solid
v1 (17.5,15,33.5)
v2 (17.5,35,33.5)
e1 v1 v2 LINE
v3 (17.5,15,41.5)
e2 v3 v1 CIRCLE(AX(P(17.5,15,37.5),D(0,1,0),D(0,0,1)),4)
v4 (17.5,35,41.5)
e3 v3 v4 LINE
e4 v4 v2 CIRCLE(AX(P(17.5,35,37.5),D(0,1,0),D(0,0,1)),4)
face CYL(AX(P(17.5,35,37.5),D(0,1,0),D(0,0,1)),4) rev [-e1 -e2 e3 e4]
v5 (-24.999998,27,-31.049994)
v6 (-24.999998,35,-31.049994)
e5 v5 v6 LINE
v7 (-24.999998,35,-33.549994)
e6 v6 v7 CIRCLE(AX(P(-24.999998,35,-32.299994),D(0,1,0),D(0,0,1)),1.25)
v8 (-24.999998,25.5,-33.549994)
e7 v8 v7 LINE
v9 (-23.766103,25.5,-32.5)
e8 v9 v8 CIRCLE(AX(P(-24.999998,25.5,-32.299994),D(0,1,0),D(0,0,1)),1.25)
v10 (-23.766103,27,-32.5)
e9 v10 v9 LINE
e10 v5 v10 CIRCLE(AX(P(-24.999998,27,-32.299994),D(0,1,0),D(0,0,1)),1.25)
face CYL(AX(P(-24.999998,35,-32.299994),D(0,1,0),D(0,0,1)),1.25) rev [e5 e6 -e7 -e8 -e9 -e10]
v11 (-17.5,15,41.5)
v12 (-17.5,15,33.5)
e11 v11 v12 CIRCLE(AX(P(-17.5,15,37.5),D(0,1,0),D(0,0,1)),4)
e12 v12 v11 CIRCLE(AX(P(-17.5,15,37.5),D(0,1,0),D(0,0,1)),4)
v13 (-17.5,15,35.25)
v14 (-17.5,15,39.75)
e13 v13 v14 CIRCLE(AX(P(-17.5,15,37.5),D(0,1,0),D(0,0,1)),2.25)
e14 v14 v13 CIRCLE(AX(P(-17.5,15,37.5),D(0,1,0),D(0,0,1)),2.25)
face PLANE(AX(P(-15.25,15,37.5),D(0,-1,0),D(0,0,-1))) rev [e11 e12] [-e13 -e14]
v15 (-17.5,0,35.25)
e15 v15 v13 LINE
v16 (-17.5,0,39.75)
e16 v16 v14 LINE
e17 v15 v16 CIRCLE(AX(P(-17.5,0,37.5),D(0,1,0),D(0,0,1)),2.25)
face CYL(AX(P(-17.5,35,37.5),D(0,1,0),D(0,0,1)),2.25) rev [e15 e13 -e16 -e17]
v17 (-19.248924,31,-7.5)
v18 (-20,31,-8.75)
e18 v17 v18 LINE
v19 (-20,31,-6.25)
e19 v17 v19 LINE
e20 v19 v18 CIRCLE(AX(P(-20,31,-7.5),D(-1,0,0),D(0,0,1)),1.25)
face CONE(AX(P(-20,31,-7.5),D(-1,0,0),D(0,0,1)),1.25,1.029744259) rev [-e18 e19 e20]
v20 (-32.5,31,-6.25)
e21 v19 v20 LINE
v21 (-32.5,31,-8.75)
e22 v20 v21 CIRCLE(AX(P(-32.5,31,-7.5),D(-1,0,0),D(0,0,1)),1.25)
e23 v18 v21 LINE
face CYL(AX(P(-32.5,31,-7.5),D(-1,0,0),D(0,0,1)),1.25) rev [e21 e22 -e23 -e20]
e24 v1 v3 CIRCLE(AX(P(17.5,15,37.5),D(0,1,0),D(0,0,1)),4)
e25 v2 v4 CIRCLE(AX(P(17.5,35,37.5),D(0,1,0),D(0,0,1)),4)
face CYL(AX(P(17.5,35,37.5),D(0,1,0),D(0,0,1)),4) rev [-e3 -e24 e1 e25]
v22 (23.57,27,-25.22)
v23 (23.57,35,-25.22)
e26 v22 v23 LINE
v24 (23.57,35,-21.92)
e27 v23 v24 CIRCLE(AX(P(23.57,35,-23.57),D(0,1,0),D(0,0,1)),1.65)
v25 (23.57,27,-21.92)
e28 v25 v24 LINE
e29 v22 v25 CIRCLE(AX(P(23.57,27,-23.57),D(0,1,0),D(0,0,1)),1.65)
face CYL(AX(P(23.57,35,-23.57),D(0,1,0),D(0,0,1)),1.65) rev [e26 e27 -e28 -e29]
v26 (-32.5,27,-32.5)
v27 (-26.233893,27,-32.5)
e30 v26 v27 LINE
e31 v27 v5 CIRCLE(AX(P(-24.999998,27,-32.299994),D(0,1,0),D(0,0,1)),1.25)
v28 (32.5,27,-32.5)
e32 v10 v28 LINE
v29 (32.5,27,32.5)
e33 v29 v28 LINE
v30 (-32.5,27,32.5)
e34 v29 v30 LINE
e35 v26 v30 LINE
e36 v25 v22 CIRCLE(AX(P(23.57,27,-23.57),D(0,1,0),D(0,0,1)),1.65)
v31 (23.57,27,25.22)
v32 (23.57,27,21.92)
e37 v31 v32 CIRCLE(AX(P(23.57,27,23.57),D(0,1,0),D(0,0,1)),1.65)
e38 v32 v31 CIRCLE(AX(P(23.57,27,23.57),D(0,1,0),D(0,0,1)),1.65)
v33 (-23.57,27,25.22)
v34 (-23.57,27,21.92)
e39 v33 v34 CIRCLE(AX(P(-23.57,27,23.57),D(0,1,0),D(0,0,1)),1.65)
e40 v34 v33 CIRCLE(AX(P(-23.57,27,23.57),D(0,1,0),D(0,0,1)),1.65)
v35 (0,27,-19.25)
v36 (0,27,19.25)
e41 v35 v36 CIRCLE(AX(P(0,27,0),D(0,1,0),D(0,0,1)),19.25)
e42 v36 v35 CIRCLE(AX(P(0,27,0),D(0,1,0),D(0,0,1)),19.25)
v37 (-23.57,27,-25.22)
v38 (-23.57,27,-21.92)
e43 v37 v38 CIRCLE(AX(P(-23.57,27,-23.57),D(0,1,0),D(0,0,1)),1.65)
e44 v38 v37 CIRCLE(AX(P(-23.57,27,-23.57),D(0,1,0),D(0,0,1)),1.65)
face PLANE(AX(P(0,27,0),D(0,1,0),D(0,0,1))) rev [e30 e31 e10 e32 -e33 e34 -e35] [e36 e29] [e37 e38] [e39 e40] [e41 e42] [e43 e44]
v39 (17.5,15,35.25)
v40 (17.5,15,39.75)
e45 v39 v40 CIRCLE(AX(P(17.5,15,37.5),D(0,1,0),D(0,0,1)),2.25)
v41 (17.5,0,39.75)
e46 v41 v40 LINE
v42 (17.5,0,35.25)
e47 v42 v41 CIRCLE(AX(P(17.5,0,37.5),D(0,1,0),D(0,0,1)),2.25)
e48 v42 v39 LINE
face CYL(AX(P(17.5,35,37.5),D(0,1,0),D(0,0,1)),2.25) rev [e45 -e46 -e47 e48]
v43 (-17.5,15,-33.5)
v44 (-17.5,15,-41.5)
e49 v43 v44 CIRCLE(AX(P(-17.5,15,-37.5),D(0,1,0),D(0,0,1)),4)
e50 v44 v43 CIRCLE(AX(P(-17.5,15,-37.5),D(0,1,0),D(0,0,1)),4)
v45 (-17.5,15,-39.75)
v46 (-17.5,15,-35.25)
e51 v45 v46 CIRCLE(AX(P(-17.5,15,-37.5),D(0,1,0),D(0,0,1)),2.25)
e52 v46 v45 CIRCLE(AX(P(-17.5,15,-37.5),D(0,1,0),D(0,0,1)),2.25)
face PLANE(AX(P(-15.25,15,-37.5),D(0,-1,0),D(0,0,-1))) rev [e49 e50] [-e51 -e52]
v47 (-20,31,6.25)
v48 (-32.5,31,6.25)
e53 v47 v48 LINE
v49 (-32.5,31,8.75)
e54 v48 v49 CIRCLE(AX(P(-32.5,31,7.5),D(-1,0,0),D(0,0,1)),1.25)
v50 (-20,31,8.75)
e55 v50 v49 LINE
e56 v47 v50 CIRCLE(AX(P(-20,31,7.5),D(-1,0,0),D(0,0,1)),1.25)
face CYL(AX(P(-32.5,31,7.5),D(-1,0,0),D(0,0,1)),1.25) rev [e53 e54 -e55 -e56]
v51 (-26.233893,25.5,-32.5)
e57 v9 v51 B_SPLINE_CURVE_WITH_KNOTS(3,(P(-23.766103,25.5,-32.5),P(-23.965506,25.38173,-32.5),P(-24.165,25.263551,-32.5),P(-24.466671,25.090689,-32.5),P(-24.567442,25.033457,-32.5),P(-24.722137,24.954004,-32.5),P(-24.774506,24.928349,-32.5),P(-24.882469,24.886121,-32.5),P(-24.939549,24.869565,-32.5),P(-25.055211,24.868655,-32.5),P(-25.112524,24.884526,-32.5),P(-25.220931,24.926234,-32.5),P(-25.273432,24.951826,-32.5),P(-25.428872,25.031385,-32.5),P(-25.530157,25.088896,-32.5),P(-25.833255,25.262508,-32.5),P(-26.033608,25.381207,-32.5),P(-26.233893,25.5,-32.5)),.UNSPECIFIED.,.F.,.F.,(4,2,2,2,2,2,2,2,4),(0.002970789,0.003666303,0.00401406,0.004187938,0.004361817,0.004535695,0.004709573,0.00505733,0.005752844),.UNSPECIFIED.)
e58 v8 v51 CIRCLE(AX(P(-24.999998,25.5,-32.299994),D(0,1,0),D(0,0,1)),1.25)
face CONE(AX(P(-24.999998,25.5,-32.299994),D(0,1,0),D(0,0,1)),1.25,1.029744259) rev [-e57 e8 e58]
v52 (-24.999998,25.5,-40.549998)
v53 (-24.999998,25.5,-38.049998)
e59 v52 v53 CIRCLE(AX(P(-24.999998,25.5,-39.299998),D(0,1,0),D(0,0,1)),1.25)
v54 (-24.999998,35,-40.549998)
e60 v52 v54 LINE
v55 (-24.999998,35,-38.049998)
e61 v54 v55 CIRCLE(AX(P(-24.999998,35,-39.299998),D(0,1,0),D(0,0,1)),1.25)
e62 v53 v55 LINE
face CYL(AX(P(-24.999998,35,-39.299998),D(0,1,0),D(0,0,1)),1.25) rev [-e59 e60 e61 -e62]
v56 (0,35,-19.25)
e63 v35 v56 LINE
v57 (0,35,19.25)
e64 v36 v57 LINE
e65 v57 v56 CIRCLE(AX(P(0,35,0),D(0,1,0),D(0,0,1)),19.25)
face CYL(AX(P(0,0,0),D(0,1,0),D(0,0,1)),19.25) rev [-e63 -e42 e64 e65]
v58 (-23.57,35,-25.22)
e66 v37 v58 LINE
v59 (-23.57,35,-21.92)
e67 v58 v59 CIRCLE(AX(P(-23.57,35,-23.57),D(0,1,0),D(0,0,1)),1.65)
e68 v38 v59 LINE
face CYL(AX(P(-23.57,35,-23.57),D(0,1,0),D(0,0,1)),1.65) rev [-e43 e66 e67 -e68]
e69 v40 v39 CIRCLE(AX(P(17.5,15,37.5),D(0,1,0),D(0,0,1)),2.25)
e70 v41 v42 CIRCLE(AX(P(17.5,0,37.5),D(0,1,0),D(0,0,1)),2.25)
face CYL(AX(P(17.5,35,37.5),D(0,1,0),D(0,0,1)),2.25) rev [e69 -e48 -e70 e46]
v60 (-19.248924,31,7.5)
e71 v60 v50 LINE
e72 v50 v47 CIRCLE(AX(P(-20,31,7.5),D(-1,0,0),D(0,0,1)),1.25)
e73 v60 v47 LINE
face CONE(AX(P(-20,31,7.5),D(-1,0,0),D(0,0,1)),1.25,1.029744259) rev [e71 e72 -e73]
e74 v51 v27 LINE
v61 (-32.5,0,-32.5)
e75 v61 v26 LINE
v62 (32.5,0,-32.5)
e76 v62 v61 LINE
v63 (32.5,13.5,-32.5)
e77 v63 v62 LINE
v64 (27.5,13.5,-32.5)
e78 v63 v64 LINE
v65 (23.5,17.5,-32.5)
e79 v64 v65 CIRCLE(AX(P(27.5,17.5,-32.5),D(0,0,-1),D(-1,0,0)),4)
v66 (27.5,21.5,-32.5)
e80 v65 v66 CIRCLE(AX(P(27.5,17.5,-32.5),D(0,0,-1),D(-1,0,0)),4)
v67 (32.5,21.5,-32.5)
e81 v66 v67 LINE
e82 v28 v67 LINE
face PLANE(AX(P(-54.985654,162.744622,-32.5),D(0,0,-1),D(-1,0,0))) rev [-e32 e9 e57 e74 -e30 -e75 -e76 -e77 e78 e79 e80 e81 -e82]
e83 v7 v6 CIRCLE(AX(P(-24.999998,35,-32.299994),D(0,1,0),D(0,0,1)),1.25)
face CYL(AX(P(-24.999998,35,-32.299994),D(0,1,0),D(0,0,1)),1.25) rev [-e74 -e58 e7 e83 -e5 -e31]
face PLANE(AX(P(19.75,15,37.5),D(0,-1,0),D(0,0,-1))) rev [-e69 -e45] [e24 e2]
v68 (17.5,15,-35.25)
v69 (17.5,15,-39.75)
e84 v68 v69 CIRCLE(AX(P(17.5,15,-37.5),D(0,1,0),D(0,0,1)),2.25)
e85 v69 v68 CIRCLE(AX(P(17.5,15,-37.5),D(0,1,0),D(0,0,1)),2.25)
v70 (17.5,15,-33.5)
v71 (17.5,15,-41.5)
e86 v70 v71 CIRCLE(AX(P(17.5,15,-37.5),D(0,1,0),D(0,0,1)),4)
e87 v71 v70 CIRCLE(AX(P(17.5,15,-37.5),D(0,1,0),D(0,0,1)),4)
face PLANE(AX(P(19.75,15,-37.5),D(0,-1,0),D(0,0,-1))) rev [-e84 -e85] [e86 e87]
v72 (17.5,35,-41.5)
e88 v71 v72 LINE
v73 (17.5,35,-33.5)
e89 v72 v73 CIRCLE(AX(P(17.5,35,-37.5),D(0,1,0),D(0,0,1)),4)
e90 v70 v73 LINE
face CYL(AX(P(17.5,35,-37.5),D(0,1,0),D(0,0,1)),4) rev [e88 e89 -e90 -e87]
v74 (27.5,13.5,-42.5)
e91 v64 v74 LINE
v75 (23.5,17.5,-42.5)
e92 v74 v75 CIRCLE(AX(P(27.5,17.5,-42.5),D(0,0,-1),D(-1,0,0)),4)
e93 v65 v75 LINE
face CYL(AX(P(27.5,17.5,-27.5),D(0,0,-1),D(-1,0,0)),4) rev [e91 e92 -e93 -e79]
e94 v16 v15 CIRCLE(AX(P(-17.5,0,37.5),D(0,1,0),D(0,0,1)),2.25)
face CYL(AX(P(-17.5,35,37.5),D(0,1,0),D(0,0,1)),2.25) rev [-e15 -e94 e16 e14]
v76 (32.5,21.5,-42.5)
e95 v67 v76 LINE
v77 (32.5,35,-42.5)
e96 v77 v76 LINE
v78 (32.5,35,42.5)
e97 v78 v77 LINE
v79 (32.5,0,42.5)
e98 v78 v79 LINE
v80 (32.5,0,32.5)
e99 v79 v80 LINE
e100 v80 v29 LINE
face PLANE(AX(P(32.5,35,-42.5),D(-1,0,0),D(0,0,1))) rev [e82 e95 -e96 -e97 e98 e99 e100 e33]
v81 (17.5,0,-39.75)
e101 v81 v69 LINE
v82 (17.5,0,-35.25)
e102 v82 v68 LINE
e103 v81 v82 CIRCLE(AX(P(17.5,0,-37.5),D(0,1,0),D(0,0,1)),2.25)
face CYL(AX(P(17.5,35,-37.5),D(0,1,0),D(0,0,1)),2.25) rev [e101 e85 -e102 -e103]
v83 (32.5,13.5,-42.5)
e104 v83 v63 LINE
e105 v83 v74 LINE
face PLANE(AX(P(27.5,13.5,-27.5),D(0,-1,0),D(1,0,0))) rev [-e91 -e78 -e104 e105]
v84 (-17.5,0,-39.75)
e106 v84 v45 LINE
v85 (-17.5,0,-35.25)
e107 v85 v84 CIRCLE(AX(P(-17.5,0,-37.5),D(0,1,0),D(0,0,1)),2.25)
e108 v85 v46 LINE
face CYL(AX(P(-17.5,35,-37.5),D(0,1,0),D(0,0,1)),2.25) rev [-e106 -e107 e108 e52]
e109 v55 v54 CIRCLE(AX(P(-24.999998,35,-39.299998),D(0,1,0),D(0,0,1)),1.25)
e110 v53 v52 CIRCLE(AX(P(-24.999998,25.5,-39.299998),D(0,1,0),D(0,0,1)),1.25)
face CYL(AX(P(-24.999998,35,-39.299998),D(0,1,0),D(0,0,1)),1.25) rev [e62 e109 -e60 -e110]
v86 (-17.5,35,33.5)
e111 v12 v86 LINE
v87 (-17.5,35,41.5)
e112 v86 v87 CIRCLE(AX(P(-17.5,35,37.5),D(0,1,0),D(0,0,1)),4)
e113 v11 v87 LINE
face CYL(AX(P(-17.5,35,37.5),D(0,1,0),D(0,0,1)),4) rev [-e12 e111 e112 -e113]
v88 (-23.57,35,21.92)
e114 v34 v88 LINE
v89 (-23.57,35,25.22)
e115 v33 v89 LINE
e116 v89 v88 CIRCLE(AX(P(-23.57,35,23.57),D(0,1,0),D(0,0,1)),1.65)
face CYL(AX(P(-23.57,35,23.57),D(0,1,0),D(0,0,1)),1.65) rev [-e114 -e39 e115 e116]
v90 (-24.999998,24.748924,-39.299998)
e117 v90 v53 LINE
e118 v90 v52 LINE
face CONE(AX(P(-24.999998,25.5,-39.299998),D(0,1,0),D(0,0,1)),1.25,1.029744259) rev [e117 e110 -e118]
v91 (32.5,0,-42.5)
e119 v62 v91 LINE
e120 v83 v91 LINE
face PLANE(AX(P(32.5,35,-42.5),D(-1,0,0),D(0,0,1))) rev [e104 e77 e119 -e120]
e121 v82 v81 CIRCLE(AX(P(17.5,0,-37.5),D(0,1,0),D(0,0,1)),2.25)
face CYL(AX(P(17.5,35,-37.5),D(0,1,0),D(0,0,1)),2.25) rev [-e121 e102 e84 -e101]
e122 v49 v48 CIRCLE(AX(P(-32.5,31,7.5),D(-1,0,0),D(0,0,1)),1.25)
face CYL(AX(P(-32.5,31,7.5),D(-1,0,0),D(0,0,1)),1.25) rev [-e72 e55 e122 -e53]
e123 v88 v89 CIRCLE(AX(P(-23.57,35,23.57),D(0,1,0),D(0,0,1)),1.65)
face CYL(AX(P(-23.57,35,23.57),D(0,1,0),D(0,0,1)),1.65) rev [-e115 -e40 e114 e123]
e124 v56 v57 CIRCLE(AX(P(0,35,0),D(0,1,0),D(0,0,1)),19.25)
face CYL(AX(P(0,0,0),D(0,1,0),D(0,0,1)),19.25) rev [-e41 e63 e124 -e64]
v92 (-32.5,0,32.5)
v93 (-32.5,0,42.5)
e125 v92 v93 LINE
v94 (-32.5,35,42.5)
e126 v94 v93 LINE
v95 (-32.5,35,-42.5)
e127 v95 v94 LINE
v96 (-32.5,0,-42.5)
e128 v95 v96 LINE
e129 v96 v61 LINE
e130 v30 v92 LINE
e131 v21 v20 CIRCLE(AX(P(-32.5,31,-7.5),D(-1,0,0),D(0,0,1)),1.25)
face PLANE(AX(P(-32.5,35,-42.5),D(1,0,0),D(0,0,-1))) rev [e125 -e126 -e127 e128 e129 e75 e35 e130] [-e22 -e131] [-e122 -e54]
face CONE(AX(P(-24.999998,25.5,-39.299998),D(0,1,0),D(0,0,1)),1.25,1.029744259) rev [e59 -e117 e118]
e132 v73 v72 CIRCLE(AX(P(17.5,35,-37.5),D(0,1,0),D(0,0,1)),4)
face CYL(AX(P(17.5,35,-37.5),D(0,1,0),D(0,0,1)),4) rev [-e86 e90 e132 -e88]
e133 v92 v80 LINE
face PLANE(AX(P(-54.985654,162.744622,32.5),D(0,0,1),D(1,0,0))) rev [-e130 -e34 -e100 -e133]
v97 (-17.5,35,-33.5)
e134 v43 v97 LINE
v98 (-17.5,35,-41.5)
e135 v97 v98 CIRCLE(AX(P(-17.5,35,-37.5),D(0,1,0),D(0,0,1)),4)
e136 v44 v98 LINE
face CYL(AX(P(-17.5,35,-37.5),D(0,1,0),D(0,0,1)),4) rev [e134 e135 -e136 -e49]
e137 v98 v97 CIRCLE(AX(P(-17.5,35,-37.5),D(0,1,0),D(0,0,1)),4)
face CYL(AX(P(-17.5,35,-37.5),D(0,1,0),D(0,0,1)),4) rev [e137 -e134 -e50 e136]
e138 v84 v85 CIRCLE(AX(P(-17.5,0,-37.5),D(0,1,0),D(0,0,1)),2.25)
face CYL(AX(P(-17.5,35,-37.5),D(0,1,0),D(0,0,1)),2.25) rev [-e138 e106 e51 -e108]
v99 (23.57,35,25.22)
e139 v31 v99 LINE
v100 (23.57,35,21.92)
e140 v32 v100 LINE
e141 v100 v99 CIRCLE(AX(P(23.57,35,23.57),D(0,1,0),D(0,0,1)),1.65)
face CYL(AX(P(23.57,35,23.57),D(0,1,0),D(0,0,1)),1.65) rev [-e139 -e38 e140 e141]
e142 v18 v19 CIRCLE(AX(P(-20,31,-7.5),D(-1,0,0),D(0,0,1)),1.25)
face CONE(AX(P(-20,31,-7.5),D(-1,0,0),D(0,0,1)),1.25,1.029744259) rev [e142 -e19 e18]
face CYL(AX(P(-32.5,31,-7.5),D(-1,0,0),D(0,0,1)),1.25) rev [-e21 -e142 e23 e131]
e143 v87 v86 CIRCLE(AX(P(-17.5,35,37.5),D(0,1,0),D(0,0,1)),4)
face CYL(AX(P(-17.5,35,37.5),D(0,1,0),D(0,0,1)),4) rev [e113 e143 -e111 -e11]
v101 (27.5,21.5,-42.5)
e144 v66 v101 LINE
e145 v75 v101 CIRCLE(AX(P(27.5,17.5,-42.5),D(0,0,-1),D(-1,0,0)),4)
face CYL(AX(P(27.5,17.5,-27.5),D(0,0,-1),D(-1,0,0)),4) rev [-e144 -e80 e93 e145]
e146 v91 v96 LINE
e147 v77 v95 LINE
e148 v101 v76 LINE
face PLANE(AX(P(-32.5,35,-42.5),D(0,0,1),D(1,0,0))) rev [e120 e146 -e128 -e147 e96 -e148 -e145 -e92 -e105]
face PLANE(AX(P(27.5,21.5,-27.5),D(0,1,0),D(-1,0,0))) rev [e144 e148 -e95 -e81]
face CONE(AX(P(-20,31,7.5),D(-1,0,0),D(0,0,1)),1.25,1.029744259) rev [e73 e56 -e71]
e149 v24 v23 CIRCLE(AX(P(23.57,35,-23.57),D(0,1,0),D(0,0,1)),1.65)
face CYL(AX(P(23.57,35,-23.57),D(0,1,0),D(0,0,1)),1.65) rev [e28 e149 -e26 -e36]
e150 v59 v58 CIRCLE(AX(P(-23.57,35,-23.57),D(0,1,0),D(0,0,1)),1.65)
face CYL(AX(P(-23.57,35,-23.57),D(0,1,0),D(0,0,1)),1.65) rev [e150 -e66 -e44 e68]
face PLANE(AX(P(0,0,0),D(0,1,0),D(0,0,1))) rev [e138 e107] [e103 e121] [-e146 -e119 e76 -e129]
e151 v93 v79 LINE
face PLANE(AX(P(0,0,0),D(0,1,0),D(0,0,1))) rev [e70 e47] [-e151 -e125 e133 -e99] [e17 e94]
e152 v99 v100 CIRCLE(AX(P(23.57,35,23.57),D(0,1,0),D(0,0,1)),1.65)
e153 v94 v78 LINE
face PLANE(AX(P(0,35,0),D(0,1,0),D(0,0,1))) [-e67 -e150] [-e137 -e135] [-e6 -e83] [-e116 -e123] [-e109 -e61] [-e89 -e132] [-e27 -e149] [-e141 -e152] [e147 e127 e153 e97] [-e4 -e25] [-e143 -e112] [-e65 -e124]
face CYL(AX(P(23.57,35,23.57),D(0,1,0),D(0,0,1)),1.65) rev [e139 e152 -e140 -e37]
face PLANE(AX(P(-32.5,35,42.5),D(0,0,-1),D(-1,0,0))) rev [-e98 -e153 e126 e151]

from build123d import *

# Parameters (mm, degrees)
SKETCH_1_W                = 65
SKETCH_1_H                = 85
EXTRUDE_1_DEPTH           = 35
SKETCH_2_W                = 109.971307268
SKETCH_2_H                = 65
CUT_EXTRUDE_1_DEPTH       = 27
SKETCH_3_R                = 19.25
CUT_EXTRUDE_2_DEPTH       = 64.933559263
HOLE_WIZARD_M4_1_D        = 3.3
HOLE_WIZARD_M3_1_D        = 2.5
HOLE_WIZARD_M3_1_DEPTH    = 12.5
HOLE_WIZARD_M3_1_TIP      = 0.751075774
CUT_EXTRUDE_3_DEPTH       = 15
HOLE_WIZARD_1_D           = 4.5
HOLE_WIZARD_1_CBORE_D     = 8
HOLE_WIZARD_1_CBORE_DEPTH = 20
HOLE_WIZARD_M3_3_D        = 2.5
HOLE_WIZARD_M3_3_DEPTH    = 9.5
HOLE_WIZARD_M3_3_TIP      = 0.751075774


with BuildPart() as part:
    # 草图1 → 凸台-拉伸1 (new body)
    with BuildSketch(Plane(origin=(0, 0, 0), x_dir=(1, 0, 0), z_dir=(0, 1, 0))):
        Rectangle(SKETCH_1_W, SKETCH_1_H)
    extrude(amount=EXTRUDE_1_DEPTH)

    # 草图2 → 切除-拉伸1 (cut)
    with BuildSketch(Plane.XZ):
        Rectangle(SKETCH_2_W, SKETCH_2_H)
    extrude(amount=-CUT_EXTRUDE_1_DEPTH, mode=Mode.SUBTRACT)

    # 草图3 → 切除-拉伸2 (cut, through all)
    with BuildSketch(Plane(origin=(0, 35, 0), x_dir=(1, 0, 0), z_dir=(0, 1, 0))):
        with Locations(Location((0, 0, 0), (0, 0, 270))):
            Circle(SKETCH_3_R)
    extrude(amount=-CUT_EXTRUDE_2_DEPTH, mode=Mode.SUBTRACT)

    # M4 螺纹孔1 (through all)
    with Locations(Plane(origin=(0, 35, 0), x_dir=(1, 0, 0), z_dir=(0, 1, 0))):
        with Locations((-23.57, 23.57), (23.57, 23.57), (-23.57, -23.57), (23.57, -23.57)):
            Hole(HOLE_WIZARD_M4_1_D / 2)

    # M3 螺纹孔1
    with Locations(Plane.ZY.offset(32.5)):
        with Locations((7.5, 31), (-7.5, 31)):
            Hole(HOLE_WIZARD_M3_1_D / 2, depth=HOLE_WIZARD_M3_1_DEPTH)
            with Locations((0, 0, -(HOLE_WIZARD_M3_1_DEPTH + HOLE_WIZARD_M3_1_TIP / 2))):  # 118° drill point
                Cone(0, HOLE_WIZARD_M3_1_D / 2, HOLE_WIZARD_M3_1_TIP, mode=Mode.SUBTRACT)

    # 草图10 → 切除-拉伸3 (cut)
    with BuildSketch(Plane(origin=(0, 0, -42.5), x_dir=(-1, 0, 0), z_dir=(0, 0, -1))):
        with BuildLine():
            Line((-27.5, 13.5), (-37.5, 13.5))
            ThreePointArc((-37.5, 13.5), (-41.5, 17.5), (-37.5, 21.5))
            Line((-37.5, 21.5), (-27.5, 21.5))
            ThreePointArc((-27.5, 21.5), (-23.5, 17.5), (-27.5, 13.5))
        make_face()
    extrude(amount=-CUT_EXTRUDE_3_DEPTH, mode=Mode.SUBTRACT)

    # 打孔尺寸(%根据)开槽圆柱头螺钉的类型1 (through all)
    with Locations(Plane(origin=(0, 35, 0), x_dir=(1, 0, 0), z_dir=(0, 1, 0))):
        with Locations((-17.5, 37.5), (17.5, 37.5), (-17.5, -37.5), (17.5, -37.5)):
            CounterBoreHole(HOLE_WIZARD_1_D / 2, HOLE_WIZARD_1_CBORE_D / 2, HOLE_WIZARD_1_CBORE_DEPTH)

    # M3 螺纹孔3
    with Locations(Plane(origin=(0, 35, 0), x_dir=(1, 0, 0), z_dir=(0, 1, 0))):
        with Locations((-24.99999811, 32.299994492), (-24.99999811, 39.299998272)):
            Hole(HOLE_WIZARD_M3_3_D / 2, depth=HOLE_WIZARD_M3_3_DEPTH)
            with Locations((0, 0, -(HOLE_WIZARD_M3_3_DEPTH + HOLE_WIZARD_M3_3_TIP / 2))):  # 118° drill point
                Cone(0, HOLE_WIZARD_M3_3_D / 2, HOLE_WIZARD_M3_3_TIP, mode=Mode.SUBTRACT)


solid = part.part
